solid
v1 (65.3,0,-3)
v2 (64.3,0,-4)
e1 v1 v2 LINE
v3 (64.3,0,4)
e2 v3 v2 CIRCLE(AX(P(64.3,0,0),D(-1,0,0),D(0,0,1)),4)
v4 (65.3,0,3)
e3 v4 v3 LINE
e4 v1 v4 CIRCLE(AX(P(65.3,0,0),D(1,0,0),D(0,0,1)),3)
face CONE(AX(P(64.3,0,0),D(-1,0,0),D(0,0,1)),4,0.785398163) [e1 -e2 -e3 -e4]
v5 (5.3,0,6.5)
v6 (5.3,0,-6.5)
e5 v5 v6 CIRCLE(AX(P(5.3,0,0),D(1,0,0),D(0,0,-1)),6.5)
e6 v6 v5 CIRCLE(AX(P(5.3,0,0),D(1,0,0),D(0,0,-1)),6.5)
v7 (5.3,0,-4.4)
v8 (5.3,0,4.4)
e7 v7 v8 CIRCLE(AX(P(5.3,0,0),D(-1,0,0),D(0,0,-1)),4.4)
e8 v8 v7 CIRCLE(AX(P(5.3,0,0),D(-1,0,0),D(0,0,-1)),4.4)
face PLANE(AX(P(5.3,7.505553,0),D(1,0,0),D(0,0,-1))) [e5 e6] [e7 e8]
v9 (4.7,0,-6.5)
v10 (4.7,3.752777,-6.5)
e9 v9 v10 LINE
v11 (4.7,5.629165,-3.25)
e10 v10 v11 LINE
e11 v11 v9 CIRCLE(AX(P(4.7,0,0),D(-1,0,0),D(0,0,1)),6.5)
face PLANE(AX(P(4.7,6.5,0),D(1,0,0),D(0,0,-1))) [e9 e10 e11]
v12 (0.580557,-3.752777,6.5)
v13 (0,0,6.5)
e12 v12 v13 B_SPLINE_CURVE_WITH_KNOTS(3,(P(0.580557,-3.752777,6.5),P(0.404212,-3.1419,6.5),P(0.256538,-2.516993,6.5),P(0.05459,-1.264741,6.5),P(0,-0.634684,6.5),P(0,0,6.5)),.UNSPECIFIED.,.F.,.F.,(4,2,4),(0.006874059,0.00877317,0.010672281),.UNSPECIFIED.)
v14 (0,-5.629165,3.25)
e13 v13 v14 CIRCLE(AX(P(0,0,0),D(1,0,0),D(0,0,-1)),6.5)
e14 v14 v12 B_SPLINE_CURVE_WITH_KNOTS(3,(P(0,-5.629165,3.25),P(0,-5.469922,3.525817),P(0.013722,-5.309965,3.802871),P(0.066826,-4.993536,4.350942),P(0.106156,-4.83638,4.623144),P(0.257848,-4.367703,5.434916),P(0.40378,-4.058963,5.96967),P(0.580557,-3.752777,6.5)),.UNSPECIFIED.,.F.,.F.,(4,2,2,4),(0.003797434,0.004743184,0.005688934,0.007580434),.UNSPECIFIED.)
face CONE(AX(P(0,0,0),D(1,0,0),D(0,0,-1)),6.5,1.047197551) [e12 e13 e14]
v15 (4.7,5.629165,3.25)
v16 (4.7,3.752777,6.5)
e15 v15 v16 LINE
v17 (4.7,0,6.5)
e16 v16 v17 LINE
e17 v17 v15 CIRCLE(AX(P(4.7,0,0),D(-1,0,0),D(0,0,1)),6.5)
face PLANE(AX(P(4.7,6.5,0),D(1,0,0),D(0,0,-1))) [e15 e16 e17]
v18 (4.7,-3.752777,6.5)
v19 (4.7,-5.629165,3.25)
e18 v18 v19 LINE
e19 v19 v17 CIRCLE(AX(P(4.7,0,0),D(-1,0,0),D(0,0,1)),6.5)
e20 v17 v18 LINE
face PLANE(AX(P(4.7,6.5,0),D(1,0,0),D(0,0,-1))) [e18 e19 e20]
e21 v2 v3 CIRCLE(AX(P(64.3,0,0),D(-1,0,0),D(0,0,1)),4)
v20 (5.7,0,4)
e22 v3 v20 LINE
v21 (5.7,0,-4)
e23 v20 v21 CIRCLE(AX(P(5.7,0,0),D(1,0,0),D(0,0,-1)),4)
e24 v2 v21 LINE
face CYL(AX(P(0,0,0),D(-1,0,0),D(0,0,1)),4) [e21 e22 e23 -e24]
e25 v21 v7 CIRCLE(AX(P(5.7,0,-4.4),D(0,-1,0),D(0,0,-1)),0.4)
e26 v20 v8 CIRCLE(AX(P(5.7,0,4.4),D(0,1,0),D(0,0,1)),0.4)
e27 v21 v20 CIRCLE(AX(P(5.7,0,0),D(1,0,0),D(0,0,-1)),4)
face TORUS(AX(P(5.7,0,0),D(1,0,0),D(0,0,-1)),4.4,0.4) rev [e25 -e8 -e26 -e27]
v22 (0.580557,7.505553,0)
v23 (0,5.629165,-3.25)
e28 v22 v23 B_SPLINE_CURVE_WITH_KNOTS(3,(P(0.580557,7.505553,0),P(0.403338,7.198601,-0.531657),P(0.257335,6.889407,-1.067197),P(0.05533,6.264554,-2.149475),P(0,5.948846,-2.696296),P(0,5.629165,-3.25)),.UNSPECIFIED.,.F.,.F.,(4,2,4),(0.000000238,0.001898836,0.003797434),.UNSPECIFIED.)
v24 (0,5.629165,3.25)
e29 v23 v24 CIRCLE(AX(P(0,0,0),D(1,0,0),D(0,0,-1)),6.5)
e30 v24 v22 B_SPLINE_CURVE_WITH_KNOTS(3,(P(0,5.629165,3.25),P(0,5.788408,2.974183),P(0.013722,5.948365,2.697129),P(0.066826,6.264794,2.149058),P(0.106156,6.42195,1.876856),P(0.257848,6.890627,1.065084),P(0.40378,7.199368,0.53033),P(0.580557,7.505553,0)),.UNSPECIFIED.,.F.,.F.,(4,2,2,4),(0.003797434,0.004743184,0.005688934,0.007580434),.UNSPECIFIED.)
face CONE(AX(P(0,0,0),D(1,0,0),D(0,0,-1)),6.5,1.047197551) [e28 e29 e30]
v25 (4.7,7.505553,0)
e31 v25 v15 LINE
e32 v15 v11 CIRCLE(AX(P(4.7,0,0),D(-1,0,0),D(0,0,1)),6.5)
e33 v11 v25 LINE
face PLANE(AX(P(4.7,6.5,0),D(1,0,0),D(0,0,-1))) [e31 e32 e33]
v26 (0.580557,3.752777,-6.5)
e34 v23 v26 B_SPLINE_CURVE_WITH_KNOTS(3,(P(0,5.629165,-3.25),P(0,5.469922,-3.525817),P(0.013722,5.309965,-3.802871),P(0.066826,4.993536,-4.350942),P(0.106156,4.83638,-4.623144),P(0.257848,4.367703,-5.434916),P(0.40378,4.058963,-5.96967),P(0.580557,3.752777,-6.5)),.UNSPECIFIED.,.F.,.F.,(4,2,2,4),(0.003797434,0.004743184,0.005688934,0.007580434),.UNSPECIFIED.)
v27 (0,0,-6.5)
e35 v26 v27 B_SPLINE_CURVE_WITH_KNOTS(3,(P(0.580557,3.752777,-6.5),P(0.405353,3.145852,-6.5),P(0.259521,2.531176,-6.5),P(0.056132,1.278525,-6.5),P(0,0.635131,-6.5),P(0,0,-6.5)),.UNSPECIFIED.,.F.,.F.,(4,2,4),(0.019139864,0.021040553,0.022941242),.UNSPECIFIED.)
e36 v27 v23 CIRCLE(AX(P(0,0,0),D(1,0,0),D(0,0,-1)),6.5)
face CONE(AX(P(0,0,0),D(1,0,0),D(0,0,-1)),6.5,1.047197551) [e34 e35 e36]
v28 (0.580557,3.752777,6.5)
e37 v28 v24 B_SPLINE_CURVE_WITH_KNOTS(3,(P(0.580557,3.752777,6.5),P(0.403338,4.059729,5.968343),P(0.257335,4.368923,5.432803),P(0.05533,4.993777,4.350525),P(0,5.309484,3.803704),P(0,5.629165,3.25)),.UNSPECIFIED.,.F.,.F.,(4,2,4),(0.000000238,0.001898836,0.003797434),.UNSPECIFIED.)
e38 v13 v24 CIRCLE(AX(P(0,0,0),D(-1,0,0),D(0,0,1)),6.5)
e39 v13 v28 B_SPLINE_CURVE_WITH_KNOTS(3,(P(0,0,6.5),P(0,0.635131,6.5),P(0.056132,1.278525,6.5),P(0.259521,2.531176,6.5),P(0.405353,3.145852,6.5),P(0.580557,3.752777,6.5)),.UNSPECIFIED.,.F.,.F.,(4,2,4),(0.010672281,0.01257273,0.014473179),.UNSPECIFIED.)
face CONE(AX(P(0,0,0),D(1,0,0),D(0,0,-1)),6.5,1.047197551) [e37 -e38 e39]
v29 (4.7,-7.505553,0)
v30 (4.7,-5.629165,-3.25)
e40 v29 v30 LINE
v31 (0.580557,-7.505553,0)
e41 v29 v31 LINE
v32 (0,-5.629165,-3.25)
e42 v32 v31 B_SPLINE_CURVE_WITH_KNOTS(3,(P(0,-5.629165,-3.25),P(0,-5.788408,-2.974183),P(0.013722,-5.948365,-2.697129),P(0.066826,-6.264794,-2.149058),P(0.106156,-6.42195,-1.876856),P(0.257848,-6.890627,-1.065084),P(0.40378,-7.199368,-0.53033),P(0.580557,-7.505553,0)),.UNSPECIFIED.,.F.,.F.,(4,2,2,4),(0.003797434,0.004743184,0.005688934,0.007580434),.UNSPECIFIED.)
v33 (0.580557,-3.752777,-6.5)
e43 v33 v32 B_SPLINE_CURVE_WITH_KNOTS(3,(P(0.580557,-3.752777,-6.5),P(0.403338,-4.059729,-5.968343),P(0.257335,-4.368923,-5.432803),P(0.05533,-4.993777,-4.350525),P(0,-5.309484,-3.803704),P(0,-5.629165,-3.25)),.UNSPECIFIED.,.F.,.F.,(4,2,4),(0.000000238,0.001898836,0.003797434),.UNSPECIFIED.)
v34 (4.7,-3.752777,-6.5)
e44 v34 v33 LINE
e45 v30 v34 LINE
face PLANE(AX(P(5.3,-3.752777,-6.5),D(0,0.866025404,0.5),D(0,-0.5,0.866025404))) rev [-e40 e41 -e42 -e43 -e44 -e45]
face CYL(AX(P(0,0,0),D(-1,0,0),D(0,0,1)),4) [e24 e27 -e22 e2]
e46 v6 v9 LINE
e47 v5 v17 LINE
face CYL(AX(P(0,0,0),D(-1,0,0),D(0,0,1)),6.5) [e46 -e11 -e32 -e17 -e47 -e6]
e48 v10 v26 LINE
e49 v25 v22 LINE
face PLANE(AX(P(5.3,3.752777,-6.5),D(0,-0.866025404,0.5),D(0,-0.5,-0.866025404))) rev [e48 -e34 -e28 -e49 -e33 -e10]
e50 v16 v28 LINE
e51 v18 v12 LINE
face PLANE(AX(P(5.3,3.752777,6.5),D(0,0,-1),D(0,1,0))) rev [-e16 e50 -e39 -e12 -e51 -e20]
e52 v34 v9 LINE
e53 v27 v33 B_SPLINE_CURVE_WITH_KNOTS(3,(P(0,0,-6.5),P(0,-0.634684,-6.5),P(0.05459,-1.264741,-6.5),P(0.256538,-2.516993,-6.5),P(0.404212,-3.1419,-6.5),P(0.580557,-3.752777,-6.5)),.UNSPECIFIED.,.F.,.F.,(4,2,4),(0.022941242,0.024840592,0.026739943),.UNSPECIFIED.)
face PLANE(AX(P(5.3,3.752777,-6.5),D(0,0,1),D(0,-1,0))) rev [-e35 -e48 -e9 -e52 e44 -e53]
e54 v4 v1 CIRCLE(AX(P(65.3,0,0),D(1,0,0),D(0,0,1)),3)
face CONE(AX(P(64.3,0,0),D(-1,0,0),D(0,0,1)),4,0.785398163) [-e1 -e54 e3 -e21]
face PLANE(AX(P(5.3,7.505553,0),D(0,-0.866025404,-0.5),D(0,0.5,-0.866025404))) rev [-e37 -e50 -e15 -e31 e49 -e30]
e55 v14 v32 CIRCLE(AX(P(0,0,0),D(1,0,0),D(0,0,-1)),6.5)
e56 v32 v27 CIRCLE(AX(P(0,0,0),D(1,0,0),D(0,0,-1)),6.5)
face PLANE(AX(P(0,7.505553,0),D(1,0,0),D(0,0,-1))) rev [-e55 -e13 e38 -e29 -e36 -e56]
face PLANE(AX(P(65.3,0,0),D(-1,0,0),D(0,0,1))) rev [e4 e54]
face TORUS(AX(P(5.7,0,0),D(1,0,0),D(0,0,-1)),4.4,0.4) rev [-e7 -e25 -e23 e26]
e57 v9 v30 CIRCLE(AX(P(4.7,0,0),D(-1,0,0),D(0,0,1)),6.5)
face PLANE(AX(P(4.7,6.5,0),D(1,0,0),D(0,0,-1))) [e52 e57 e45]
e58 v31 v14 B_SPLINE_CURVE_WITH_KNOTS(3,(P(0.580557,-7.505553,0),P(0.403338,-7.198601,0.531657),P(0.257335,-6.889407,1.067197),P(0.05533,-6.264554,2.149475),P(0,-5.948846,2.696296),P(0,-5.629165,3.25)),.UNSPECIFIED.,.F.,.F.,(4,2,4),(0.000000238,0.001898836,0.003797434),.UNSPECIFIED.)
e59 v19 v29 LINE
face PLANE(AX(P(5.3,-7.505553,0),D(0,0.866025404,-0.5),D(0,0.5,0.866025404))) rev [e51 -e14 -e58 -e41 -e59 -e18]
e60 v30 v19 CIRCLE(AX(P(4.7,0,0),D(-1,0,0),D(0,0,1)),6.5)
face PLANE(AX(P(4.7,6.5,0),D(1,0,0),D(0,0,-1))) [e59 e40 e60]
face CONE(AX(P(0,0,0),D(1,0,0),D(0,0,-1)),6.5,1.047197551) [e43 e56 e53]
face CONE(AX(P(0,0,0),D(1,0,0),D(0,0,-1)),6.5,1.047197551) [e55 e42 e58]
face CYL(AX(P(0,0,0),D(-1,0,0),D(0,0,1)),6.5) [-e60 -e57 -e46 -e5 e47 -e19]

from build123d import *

# Parameters (mm, degrees)
BASE_EXTRUDE_DEPTH = 5.3
SKETCH4_W          = 0.6
SKETCH4_H          = 11.005553499
CHAMFER_2_SIZE     = 1
FILLET_2_R         = 0.4


with BuildPart() as part:
    # Sketch1 → Base-Extrude (new body)
    with BuildSketch(Plane(origin=(0, 0, 0), x_dir=(0, 0, -1), z_dir=(1, 0, 0))):
        Polygon((6.5, 3.75277675), (6.5, -3.75277675), (0, -7.505553499), (-6.5, -3.75277675), (-6.5, 3.75277675), (0, 7.505553499), align=None)
    extrude(amount=BASE_EXTRUDE_DEPTH)

    # Sketch2 → Boss-Revolve1 (revolve)
    with BuildSketch(Plane.XY, mode=Mode.PRIVATE) as boss_revolve1_sk:
        Polygon((0, 0), (65.3, 0), (65.3, 2.9175), (65.3, 4), (7.791693541, 4), (0, 4), align=None)
    revolve(boss_revolve1_sk.sketch.rotate(Axis((0, 0, 0), (1, 0, 0)), 90), axis=Axis((0, 0, 0), (1, 0, 0)))

    # Sketch3 → Cut-Revolve1 (revolve, cut)
    with BuildSketch(Plane.XY):
        Polygon((0, 6.5), (3.46730793, 12.505553499), (3.46730793, 17.505553499), (-10, 17.505553499), (-10, 6.5), align=None)
    revolve(axis=Axis((0, 0, 0), (1, 0, 0)), mode=Mode.SUBTRACT)

    # Sketch5 → Cut-Revolve2 (revolve, cut)
    with BuildSketch(Plane.XY):
        Polygon((5.3, 6.5), (1.83269207, 12.505553499), (1.83269207, 17.505553499), (11.83269207, 17.505553499), (11.83269207, 6.5), align=None)
    revolve(axis=Axis((0, 0, 0), (1, 0, 0)), mode=Mode.SUBTRACT)

    # Sketch4 → Cut-Revolve3 (revolve, cut)
    with BuildSketch(Plane.XY, mode=Mode.PRIVATE) as cut_revolve3_sk:
        with Locations((5, 12.00277675)):
            Rectangle(SKETCH4_W, SKETCH4_H)
    revolve(cut_revolve3_sk.sketch.rotate(Axis((0, 0, 0), (1, 0, 0)), 270), axis=Axis((0, 0, 0), (1, 0, 0)), mode=Mode.SUBTRACT)

    # Chamfer 2
    chamfer_2_edges = [part.edges().sort_by_distance(p)[0] for p in [
        (65.3, 0, -4),
    ]]
    chamfer(chamfer_2_edges, length=CHAMFER_2_SIZE)

    # Fillet 2
    fillet_2_edges = [part.edges().sort_by_distance(p)[0] for p in [
        (5.3, 0, -4),
    ]]
    fillet(fillet_2_edges, radius=FILLET_2_R)


solid = part.part
